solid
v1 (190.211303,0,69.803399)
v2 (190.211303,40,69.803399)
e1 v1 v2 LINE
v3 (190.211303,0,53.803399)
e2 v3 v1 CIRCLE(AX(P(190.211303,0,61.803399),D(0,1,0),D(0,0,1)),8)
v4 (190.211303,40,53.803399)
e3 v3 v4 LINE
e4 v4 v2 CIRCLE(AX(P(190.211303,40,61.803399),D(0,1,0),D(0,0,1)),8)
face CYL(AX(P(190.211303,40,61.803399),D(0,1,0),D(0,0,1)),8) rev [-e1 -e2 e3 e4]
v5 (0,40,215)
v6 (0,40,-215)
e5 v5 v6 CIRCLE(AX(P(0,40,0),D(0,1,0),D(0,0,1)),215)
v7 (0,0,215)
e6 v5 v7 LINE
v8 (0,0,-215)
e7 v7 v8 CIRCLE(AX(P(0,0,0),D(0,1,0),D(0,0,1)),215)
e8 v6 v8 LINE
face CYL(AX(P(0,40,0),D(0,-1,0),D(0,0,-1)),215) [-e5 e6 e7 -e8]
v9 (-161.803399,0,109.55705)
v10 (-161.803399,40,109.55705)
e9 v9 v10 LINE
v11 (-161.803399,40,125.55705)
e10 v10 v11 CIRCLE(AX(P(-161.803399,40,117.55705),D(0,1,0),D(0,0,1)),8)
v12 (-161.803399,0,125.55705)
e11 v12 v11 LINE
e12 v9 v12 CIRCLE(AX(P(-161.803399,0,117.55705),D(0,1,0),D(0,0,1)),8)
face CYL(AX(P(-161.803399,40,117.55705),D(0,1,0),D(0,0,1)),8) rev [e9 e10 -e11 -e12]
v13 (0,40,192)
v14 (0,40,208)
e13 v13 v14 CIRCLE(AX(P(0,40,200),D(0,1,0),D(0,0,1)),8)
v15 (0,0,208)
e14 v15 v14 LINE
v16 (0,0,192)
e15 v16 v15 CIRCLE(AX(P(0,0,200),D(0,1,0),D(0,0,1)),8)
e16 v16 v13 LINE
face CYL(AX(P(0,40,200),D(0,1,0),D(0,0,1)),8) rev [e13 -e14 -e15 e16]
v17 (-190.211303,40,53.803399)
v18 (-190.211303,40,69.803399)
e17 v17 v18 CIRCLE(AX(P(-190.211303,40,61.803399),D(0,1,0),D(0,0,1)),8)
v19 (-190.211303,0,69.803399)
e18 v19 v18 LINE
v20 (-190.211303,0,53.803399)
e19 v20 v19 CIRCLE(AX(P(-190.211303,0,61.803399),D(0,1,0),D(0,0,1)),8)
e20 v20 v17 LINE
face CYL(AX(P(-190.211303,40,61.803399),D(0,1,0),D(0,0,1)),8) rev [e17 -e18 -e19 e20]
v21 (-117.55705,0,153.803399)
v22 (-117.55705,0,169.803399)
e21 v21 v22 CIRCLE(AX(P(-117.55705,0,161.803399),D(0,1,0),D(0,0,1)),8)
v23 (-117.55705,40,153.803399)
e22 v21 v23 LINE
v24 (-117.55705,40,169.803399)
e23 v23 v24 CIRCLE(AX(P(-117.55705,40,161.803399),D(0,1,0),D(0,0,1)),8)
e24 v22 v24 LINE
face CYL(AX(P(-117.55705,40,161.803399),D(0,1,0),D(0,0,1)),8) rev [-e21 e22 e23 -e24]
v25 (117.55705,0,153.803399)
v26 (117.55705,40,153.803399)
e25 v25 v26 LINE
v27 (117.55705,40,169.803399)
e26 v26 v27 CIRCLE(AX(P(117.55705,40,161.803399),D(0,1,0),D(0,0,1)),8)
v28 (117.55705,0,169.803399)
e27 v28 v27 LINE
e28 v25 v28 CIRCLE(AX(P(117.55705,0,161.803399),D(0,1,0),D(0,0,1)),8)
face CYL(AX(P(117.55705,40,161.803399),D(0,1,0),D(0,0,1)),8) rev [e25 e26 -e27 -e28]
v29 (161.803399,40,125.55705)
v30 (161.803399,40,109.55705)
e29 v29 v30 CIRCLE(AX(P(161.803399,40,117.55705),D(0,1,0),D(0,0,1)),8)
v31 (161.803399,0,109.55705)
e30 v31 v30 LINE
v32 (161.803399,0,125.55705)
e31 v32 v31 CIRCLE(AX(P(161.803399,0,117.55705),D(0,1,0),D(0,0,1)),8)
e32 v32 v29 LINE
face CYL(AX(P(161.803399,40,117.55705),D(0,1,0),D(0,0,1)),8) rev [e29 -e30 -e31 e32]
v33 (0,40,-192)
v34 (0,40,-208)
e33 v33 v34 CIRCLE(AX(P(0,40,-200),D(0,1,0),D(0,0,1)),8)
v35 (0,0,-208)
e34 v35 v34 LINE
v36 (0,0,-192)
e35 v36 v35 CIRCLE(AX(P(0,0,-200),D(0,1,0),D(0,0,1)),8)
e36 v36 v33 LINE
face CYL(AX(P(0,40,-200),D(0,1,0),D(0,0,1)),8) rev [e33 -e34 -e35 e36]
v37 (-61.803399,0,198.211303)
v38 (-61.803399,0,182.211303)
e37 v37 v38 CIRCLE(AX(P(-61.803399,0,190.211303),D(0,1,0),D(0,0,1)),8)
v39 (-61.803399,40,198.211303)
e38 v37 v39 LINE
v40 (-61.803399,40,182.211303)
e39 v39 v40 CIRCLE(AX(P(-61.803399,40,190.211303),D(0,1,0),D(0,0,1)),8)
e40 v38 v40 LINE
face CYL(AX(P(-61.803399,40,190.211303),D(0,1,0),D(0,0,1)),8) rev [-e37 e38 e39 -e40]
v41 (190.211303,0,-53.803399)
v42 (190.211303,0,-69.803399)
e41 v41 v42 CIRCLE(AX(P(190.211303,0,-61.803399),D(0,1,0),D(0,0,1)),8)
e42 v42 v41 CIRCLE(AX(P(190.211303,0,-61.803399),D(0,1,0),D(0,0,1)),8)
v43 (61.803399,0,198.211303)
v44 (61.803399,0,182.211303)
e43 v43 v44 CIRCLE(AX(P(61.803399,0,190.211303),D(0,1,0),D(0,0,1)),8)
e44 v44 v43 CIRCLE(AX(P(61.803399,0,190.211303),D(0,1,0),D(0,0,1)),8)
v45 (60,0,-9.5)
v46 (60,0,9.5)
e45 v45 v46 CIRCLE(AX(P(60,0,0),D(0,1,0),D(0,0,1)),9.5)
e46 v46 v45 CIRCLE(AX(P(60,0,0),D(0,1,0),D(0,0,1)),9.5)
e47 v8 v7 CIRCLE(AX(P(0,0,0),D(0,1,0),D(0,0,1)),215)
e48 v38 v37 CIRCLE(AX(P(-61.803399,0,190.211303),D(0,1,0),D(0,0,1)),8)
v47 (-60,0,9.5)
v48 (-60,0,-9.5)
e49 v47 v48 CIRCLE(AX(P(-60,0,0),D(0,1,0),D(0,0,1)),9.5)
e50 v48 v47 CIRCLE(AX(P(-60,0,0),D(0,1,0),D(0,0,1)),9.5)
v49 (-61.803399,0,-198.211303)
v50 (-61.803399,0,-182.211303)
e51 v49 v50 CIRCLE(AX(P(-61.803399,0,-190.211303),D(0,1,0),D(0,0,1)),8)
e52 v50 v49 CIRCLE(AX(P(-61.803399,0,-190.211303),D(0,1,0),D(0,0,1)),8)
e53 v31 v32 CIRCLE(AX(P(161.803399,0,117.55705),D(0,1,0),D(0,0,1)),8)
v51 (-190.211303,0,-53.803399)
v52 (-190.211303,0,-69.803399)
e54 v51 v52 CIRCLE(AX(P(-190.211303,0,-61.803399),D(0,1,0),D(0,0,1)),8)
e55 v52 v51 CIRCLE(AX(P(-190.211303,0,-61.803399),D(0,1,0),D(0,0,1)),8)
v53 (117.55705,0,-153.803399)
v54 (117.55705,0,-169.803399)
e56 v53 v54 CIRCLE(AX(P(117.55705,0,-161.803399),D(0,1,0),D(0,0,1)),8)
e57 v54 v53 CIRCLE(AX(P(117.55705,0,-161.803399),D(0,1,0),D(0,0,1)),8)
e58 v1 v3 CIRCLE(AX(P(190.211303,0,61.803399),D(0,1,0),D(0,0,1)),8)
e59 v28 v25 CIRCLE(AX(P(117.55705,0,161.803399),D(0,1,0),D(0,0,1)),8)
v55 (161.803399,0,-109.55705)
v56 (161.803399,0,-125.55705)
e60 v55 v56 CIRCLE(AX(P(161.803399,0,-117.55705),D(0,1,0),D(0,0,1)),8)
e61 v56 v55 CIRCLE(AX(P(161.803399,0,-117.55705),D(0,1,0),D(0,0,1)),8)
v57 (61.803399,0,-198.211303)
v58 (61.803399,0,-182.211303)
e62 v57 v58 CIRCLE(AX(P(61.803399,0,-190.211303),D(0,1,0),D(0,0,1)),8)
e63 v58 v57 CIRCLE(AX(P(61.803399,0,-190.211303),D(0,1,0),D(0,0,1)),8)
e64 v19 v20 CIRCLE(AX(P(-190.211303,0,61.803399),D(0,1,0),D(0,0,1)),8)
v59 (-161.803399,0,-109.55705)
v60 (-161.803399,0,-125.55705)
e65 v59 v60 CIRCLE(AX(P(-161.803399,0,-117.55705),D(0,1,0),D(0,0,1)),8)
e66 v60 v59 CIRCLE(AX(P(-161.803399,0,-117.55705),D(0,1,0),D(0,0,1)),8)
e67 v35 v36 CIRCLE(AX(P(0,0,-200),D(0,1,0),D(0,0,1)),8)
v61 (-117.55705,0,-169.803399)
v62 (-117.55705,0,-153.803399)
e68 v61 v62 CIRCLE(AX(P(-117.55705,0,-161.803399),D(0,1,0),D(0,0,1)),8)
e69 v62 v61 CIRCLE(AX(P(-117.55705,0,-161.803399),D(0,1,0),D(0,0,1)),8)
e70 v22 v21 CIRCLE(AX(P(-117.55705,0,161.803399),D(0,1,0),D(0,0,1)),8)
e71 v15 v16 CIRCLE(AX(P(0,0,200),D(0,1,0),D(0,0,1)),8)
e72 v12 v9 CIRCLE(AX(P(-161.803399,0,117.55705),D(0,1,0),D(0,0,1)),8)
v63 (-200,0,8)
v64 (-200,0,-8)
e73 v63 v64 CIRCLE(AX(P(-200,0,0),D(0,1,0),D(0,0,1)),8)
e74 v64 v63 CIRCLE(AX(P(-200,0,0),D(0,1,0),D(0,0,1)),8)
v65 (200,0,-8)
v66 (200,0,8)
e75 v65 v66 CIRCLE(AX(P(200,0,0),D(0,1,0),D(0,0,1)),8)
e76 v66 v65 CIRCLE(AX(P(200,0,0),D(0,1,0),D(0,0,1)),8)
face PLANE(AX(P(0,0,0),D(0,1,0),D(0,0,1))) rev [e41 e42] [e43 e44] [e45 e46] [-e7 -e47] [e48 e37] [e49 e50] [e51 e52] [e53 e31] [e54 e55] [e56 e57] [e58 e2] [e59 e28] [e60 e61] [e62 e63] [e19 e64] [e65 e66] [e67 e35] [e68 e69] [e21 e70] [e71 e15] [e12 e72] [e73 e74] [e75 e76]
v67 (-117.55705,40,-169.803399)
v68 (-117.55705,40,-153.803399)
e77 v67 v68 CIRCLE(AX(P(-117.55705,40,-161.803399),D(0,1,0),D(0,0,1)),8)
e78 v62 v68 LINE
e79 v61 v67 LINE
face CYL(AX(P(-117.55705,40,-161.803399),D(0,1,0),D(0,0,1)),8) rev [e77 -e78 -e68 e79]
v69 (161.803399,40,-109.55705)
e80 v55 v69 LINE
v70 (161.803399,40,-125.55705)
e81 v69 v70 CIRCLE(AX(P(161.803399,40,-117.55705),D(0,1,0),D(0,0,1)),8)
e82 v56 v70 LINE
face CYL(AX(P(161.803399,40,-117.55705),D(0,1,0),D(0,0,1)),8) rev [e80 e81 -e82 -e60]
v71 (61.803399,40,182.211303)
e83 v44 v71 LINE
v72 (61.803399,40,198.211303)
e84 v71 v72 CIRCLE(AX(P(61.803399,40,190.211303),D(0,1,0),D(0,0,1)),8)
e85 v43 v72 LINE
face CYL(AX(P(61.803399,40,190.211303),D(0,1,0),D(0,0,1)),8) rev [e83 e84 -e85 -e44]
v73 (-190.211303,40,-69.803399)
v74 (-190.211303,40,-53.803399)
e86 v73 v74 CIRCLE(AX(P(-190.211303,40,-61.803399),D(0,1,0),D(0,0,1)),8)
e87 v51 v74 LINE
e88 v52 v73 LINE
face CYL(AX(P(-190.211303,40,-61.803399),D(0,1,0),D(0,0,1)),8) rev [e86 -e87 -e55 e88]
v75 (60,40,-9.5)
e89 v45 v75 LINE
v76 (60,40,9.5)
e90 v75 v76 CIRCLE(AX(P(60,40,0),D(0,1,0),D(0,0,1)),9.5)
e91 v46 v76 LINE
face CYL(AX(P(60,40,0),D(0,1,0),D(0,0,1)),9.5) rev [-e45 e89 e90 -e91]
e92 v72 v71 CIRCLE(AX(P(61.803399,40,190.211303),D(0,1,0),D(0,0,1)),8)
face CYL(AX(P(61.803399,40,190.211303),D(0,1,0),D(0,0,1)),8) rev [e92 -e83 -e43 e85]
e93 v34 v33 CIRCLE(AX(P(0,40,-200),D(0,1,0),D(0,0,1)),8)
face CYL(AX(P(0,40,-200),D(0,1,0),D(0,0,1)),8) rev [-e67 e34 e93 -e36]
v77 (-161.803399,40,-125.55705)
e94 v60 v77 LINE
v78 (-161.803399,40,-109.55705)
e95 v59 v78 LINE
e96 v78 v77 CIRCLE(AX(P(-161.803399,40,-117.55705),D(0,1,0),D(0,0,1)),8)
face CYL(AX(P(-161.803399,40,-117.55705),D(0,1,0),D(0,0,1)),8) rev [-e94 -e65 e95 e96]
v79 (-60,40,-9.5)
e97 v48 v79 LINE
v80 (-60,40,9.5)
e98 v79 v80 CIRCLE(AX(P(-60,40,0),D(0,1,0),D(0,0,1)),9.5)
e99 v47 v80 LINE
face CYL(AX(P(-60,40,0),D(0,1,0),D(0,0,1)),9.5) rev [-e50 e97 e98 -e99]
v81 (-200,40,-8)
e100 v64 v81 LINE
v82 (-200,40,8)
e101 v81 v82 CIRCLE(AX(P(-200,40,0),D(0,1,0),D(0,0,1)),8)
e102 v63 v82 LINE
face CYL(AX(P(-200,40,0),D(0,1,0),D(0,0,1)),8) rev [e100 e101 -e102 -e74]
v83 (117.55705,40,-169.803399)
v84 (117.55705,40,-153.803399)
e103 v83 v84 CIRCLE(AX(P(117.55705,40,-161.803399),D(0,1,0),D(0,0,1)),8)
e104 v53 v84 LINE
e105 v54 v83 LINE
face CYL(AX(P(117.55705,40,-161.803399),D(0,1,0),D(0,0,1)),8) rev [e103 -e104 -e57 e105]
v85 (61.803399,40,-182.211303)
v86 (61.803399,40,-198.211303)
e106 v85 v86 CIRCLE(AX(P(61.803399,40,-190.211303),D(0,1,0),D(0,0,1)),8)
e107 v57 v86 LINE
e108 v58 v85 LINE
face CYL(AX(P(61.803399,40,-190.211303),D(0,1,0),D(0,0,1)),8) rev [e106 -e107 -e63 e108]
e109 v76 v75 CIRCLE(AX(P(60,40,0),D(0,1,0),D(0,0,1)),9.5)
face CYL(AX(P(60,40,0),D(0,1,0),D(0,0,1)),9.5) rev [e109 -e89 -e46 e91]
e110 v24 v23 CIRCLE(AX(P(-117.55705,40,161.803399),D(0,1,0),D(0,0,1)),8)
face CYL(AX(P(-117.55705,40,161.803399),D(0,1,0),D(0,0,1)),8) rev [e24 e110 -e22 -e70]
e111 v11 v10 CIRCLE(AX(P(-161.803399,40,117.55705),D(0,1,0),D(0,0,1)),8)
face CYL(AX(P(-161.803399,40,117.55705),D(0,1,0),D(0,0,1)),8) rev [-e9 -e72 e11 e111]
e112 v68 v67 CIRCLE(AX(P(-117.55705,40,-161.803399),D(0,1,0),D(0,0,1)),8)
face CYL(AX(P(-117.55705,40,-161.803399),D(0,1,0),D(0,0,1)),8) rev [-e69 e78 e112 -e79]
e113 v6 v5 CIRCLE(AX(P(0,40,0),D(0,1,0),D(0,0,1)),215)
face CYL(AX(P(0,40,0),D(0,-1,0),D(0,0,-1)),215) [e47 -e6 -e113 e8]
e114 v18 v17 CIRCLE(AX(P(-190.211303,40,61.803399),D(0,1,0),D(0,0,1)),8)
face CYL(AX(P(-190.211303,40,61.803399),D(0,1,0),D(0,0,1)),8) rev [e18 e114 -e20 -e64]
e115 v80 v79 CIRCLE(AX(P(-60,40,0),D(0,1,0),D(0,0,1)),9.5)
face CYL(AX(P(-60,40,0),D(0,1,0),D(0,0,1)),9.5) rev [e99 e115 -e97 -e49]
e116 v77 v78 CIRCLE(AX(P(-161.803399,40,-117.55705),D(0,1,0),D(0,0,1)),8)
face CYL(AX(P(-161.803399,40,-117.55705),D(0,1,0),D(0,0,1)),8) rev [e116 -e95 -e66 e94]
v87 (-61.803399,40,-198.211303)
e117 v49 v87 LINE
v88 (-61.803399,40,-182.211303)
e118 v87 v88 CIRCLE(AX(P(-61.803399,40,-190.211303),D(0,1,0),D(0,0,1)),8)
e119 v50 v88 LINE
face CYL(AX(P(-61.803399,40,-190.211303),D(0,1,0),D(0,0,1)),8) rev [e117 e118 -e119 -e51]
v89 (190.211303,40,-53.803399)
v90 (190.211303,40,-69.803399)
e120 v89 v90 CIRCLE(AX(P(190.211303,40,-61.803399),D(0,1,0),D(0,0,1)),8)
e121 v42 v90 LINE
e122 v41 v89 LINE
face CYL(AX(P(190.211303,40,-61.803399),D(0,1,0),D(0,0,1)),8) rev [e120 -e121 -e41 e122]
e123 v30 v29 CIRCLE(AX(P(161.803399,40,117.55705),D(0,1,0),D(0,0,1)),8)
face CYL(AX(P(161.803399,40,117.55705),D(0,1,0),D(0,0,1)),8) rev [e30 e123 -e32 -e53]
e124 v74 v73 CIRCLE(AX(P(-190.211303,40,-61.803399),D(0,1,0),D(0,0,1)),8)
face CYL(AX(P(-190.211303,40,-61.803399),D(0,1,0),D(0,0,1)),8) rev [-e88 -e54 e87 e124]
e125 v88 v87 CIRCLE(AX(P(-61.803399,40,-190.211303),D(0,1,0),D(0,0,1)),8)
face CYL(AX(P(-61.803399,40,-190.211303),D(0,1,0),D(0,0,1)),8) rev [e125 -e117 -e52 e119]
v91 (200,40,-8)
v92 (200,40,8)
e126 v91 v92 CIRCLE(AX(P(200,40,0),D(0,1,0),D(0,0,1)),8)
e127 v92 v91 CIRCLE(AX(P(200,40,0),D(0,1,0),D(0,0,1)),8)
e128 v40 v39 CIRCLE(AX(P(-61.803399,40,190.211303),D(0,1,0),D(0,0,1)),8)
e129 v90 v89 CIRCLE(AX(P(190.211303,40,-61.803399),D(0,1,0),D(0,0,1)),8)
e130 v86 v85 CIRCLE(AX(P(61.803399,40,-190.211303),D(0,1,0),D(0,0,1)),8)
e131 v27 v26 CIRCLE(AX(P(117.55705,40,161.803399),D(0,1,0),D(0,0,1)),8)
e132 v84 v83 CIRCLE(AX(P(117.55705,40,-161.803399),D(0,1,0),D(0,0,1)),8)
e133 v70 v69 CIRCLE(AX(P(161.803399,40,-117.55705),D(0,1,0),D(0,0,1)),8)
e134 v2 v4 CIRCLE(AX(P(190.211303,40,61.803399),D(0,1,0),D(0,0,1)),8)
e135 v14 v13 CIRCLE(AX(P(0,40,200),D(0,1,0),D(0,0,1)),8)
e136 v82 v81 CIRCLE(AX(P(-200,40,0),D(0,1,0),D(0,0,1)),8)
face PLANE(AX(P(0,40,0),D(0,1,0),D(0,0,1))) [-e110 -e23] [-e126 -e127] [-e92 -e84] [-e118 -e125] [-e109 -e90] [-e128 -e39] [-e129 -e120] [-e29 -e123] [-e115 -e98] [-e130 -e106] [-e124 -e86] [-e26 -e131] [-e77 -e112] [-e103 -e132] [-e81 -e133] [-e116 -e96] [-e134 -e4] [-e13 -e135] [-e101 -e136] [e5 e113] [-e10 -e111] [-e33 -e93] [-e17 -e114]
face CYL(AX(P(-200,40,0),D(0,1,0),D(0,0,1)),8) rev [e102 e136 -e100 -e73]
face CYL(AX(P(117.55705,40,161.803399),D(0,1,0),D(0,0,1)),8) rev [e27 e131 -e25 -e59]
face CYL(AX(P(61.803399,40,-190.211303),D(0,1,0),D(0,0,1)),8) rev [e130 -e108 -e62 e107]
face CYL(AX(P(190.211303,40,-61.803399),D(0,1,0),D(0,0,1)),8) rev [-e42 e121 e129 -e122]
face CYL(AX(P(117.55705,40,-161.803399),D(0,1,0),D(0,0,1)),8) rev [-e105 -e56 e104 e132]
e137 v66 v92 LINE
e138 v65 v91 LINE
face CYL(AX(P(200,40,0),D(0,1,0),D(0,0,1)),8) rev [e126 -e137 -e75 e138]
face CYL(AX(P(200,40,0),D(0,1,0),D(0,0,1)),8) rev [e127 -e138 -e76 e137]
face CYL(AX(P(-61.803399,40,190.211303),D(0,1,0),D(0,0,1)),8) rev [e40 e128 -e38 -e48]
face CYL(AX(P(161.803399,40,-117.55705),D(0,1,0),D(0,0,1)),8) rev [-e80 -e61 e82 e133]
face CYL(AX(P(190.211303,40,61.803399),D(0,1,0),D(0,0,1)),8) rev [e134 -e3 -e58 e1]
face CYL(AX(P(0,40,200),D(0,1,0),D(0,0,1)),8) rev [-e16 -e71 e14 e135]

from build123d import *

# Parameters (mm, degrees)
SKETCH1_R                  = 215
BOSS_EXTRUDE1_DEPTH        = 40
F_16_0_16_DIAMETER_HOLE1_D = 16
G1_2_TAPPED_HOLE1_D        = 19


with BuildPart() as part:
    # Sketch1 → Boss-Extrude1 (new body)
    with BuildSketch(Plane(origin=(0, 0, 0), x_dir=(1, 0, 0), z_dir=(0, 1, 0))):
        with Locations(Location((0, 0, 0), (0, 0, 270))):
            Circle(SKETCH1_R)
    extrude(amount=BOSS_EXTRUDE1_DEPTH)

    # Ø16.0 (16) Diameter Hole1 (through all)
    with Locations(Plane(origin=(0, 40, 0), x_dir=(1, 0, 0), z_dir=(0, 1, 0))):
        with Locations((200, 0), (190.211303259, -61.803398875), (161.803398875, -117.557050458), (117.557050458, -161.803398875), (61.803398875, -190.211303259), (0, -200), (-61.803398875, -190.211303259), (-117.557050458, -161.803398875), (-161.803398875, -117.557050458), (-190.211303259, -61.803398875), (-200, 0), (-190.211303259, 61.803398875), (-161.803398875, 117.557050458), (-117.557050458, 161.803398875), (-61.803398875, 190.211303259), (0, 200), (61.803398875, 190.211303259), (117.557050458, 161.803398875), (161.803398875, 117.557050458), (190.211303259, 61.803398875)):
            Hole(F_16_0_16_DIAMETER_HOLE1_D / 2)

    # G1/2 Tapped Hole1 (through all)
    with Locations(Plane(origin=(0, 40, 0), x_dir=(1, 0, 0), z_dir=(0, 1, 0))):
        with Locations((-60, 0), (60, 0)):
            Hole(G1_2_TAPPED_HOLE1_D / 2)


solid = part.part
